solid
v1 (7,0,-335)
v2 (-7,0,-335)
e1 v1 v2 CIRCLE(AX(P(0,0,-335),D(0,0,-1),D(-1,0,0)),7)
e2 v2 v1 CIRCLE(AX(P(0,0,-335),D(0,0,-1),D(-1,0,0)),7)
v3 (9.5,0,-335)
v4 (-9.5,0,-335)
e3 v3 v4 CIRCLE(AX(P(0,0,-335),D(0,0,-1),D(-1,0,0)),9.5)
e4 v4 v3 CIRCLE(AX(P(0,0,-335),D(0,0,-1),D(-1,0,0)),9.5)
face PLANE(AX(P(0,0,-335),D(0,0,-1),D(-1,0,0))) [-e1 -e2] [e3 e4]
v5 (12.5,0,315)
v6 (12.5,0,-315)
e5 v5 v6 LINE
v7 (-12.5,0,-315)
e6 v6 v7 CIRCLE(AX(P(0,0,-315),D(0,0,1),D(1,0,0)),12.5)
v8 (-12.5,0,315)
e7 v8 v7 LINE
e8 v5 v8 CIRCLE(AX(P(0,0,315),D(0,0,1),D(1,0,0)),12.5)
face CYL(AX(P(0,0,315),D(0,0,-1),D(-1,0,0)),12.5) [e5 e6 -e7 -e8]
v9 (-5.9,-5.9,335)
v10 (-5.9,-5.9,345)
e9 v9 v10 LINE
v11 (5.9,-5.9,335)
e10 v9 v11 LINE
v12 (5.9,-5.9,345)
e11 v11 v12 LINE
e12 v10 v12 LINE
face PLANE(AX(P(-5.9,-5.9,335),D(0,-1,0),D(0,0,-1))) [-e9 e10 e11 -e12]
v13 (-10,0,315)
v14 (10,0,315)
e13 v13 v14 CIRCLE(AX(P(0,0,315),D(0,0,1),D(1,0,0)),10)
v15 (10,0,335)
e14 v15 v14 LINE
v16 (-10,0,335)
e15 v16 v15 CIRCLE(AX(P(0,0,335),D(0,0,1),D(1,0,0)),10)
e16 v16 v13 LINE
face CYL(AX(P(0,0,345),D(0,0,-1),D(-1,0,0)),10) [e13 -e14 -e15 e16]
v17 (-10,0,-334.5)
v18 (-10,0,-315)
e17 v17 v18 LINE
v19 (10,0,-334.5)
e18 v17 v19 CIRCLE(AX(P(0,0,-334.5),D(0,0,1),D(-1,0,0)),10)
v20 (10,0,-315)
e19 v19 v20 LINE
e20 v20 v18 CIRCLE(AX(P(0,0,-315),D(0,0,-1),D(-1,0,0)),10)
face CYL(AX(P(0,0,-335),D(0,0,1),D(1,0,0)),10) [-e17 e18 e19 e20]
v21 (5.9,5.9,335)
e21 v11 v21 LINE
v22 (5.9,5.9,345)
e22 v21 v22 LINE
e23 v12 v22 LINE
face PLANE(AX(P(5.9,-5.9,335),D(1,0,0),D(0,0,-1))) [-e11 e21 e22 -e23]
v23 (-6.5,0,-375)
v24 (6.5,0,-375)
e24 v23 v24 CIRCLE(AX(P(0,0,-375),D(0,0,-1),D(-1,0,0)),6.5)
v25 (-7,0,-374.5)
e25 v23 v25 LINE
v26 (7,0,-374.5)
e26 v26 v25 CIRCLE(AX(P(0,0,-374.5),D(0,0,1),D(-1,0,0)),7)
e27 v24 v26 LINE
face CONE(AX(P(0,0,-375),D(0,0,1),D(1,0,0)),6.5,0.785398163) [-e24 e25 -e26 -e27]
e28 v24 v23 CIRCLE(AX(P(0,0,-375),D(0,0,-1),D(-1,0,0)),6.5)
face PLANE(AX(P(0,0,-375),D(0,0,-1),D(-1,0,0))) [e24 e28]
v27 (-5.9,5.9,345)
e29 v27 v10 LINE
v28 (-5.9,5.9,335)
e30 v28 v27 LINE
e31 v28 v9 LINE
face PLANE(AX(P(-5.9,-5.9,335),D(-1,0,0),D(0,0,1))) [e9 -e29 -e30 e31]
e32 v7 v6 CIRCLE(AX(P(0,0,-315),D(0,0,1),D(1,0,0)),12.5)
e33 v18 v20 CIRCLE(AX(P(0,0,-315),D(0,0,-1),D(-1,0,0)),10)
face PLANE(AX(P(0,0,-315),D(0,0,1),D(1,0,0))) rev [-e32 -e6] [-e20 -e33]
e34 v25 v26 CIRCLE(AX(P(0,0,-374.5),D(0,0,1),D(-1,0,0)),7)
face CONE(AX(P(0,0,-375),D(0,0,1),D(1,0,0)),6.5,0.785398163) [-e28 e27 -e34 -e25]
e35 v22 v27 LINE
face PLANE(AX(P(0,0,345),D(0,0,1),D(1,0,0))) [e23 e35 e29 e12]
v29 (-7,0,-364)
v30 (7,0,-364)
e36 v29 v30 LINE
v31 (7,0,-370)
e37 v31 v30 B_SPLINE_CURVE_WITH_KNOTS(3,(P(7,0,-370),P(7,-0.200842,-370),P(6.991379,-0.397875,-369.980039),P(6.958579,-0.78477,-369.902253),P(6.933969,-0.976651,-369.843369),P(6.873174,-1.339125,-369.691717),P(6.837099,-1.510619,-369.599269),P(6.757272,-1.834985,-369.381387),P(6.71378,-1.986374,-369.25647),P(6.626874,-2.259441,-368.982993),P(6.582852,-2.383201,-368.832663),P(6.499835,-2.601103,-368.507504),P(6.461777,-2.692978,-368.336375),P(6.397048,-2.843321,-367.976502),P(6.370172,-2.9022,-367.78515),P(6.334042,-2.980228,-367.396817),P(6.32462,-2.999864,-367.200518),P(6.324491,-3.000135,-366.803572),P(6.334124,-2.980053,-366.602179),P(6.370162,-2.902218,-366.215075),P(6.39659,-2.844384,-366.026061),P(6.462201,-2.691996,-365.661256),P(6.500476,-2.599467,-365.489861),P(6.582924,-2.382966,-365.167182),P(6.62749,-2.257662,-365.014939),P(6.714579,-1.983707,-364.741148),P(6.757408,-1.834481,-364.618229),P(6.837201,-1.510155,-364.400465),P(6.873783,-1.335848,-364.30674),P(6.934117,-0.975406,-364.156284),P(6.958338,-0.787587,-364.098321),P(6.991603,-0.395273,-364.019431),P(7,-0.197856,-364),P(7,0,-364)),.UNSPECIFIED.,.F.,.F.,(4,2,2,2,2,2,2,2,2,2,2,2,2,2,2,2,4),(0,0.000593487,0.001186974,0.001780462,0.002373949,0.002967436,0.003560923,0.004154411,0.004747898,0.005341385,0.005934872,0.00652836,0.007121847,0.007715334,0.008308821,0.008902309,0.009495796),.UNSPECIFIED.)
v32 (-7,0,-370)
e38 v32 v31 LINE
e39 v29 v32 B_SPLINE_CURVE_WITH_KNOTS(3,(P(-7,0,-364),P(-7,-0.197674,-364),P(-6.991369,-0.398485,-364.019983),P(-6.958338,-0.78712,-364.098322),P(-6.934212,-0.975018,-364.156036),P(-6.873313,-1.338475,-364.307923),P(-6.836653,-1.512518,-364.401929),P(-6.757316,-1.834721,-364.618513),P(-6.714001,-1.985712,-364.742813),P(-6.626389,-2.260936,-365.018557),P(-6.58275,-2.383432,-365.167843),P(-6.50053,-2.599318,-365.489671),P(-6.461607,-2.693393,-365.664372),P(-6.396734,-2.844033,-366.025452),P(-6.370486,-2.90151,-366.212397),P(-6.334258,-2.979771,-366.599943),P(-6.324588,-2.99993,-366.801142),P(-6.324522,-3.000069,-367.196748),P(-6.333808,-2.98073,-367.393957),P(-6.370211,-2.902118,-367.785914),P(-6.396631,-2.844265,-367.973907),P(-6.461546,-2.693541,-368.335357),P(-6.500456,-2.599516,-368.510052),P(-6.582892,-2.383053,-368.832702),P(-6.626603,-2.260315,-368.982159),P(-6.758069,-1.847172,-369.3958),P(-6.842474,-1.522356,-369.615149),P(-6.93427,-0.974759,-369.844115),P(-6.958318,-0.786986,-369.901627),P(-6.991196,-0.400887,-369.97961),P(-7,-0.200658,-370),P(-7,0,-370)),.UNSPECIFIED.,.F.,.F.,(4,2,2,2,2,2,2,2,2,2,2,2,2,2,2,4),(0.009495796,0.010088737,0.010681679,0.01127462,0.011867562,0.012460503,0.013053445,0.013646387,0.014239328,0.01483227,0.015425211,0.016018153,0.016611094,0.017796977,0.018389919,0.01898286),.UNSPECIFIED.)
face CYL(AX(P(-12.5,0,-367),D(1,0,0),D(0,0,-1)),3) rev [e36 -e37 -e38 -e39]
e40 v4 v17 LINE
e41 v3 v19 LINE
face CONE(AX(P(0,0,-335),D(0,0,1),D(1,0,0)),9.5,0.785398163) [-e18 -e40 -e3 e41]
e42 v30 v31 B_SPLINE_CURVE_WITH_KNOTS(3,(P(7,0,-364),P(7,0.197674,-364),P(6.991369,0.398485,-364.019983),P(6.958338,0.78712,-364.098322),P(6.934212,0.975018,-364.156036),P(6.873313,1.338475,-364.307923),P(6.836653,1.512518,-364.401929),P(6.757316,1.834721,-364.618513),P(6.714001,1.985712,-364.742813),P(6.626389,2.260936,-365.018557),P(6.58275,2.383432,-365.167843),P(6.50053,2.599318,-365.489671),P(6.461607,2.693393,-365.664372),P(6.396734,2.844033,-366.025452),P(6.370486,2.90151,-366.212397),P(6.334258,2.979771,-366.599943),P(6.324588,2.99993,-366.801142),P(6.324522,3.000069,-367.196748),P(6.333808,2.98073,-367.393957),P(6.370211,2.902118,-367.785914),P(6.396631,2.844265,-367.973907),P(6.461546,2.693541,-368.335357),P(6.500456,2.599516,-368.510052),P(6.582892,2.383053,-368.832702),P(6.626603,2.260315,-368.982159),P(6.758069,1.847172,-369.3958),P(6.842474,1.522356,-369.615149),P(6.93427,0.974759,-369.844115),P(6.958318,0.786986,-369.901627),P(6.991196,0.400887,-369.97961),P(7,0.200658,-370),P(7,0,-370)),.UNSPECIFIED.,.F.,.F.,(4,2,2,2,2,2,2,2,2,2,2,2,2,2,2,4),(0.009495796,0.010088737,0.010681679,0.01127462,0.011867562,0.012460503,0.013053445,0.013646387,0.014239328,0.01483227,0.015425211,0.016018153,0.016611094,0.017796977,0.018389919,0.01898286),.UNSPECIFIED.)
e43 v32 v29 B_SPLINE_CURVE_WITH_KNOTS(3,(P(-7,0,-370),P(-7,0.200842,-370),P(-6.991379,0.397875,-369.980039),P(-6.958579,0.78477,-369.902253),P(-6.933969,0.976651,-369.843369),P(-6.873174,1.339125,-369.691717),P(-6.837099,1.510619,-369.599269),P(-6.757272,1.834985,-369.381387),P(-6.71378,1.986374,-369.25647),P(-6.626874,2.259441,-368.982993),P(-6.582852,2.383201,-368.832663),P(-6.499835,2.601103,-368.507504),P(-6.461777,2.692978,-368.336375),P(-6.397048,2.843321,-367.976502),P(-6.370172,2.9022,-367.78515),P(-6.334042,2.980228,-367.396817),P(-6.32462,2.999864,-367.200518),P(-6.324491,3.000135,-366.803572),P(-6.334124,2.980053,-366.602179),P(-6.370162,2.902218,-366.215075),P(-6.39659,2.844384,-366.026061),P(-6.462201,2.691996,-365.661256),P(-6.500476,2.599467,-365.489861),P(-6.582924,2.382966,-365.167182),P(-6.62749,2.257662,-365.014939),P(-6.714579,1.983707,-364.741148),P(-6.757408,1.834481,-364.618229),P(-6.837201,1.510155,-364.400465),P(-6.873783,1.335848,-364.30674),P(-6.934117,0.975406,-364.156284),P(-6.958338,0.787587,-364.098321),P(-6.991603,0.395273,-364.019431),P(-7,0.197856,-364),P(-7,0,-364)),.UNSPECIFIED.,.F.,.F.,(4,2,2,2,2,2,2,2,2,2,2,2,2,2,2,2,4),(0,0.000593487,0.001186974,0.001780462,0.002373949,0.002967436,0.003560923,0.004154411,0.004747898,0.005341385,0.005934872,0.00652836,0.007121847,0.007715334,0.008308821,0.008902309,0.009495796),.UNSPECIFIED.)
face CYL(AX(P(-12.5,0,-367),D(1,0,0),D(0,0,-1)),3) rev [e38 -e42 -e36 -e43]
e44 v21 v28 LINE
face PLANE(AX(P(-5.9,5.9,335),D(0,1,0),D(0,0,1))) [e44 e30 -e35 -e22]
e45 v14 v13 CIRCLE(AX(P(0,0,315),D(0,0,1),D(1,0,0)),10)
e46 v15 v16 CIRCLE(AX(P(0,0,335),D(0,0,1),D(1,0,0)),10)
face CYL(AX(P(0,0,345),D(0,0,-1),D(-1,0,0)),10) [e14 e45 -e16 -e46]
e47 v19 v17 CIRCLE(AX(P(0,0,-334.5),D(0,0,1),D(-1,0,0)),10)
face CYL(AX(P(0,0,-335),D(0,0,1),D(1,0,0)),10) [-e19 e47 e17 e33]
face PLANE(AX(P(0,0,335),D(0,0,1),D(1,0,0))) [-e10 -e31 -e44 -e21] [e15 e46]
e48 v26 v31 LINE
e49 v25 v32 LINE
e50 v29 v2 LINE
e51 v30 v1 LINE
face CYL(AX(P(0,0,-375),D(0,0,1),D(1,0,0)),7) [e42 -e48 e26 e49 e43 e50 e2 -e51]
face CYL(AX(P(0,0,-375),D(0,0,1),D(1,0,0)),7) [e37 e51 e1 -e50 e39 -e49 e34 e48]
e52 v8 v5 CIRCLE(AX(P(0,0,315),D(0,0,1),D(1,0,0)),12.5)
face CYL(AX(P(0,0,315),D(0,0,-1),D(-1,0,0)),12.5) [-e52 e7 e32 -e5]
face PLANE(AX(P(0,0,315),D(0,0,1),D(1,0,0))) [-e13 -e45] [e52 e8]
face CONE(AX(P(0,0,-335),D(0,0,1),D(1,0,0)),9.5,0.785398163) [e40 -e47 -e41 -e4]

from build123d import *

# Parameters (mm, degrees)
SKETCH_1_R               = 12.5
EXTRUDE_1_DEPTH          = 315
SKETCH_2_R               = 10
EXTRUDE_2_DEPTH          = 30
EXTRUDE_START            = 20
SKETCH_3_R               = 10
EXTRUDE_3_DEPTH          = 20
CHAMFER_1_SIZE           = 0.5
SKETCH_4_R               = 7
EXTRUDE_4_DEPTH          = 40
CHAMFER_2_SIZE           = 0.5
CUT_EXTRUDE_1_DEPTH      = 376.416435442
CUT_EXTRUDE_1_DEPTH_BACK = 376.416435442
SKETCH_5_R               = 3
SKETCH_6_R               = 16.937839691
SKETCH_6_W               = 11.8
SKETCH_6_H               = 11.8
CUT_EXTRUDE_2_DEPTH      = 10


with BuildPart() as part:
    # 草图1 → 凸台-拉伸1 (new, symmetric)
    with BuildSketch(Plane.XY):
        Circle(SKETCH_1_R)
    extrude(amount=EXTRUDE_1_DEPTH, both=True)

    # 草图2 → 凸台-拉伸2 (add)
    with BuildSketch(Plane.XY.offset(315)):
        Circle(SKETCH_2_R)
    extrude(amount=EXTRUDE_2_DEPTH)

    # 草图3 → 凸台-拉伸3 (add)
    with BuildSketch(Plane(origin=(0, 0, -315), x_dir=(-1, 0, 0), z_dir=(0, 0, -1)).offset(EXTRUDE_START)):
        with Locations(Location((0, 0, 0), (0, 0, 180))):
            Circle(SKETCH_3_R)
    extrude(amount=-EXTRUDE_3_DEPTH)

    # 倒角1
    chamfer_1_edges = [part.edges().sort_by_distance(p)[0] for p in [
        (-10, 0, -335),
        (-10, 0, 345),
    ]]
    chamfer(chamfer_1_edges, length=CHAMFER_1_SIZE)

    # 草图4 → 凸台-拉伸4 (add)
    with BuildSketch(Plane(origin=(0, 0, -335), x_dir=(-1, 0, 0), z_dir=(0, 0, -1))):
        Circle(SKETCH_4_R)
    extrude(amount=EXTRUDE_4_DEPTH)

    # 倒角2
    chamfer_2_edges = [part.edges().sort_by_distance(p)[0] for p in [
        (7, 0, -375),
    ]]
    chamfer(chamfer_2_edges, length=CHAMFER_2_SIZE)

    # 草图5 → 切除-拉伸1 (cut, two sides: drawn at the far end of the back side and taken through both)
    with BuildSketch(Plane(origin=(0, 0, 0), x_dir=(0, 0, -1), z_dir=(1, 0, 0)).offset(-CUT_EXTRUDE_1_DEPTH_BACK)):
        with Locations((367, 0)):
            Circle(SKETCH_5_R)
    extrude(amount=CUT_EXTRUDE_1_DEPTH + CUT_EXTRUDE_1_DEPTH_BACK, mode=Mode.SUBTRACT)

    # 草图6 → 切除-拉伸2 (cut)
    with BuildSketch(Plane.XY.offset(345)):
        Circle(SKETCH_6_R)
        Rectangle(SKETCH_6_W, SKETCH_6_H, mode=Mode.SUBTRACT)
    extrude(amount=-CUT_EXTRUDE_2_DEPTH, mode=Mode.SUBTRACT)


solid = part.part
